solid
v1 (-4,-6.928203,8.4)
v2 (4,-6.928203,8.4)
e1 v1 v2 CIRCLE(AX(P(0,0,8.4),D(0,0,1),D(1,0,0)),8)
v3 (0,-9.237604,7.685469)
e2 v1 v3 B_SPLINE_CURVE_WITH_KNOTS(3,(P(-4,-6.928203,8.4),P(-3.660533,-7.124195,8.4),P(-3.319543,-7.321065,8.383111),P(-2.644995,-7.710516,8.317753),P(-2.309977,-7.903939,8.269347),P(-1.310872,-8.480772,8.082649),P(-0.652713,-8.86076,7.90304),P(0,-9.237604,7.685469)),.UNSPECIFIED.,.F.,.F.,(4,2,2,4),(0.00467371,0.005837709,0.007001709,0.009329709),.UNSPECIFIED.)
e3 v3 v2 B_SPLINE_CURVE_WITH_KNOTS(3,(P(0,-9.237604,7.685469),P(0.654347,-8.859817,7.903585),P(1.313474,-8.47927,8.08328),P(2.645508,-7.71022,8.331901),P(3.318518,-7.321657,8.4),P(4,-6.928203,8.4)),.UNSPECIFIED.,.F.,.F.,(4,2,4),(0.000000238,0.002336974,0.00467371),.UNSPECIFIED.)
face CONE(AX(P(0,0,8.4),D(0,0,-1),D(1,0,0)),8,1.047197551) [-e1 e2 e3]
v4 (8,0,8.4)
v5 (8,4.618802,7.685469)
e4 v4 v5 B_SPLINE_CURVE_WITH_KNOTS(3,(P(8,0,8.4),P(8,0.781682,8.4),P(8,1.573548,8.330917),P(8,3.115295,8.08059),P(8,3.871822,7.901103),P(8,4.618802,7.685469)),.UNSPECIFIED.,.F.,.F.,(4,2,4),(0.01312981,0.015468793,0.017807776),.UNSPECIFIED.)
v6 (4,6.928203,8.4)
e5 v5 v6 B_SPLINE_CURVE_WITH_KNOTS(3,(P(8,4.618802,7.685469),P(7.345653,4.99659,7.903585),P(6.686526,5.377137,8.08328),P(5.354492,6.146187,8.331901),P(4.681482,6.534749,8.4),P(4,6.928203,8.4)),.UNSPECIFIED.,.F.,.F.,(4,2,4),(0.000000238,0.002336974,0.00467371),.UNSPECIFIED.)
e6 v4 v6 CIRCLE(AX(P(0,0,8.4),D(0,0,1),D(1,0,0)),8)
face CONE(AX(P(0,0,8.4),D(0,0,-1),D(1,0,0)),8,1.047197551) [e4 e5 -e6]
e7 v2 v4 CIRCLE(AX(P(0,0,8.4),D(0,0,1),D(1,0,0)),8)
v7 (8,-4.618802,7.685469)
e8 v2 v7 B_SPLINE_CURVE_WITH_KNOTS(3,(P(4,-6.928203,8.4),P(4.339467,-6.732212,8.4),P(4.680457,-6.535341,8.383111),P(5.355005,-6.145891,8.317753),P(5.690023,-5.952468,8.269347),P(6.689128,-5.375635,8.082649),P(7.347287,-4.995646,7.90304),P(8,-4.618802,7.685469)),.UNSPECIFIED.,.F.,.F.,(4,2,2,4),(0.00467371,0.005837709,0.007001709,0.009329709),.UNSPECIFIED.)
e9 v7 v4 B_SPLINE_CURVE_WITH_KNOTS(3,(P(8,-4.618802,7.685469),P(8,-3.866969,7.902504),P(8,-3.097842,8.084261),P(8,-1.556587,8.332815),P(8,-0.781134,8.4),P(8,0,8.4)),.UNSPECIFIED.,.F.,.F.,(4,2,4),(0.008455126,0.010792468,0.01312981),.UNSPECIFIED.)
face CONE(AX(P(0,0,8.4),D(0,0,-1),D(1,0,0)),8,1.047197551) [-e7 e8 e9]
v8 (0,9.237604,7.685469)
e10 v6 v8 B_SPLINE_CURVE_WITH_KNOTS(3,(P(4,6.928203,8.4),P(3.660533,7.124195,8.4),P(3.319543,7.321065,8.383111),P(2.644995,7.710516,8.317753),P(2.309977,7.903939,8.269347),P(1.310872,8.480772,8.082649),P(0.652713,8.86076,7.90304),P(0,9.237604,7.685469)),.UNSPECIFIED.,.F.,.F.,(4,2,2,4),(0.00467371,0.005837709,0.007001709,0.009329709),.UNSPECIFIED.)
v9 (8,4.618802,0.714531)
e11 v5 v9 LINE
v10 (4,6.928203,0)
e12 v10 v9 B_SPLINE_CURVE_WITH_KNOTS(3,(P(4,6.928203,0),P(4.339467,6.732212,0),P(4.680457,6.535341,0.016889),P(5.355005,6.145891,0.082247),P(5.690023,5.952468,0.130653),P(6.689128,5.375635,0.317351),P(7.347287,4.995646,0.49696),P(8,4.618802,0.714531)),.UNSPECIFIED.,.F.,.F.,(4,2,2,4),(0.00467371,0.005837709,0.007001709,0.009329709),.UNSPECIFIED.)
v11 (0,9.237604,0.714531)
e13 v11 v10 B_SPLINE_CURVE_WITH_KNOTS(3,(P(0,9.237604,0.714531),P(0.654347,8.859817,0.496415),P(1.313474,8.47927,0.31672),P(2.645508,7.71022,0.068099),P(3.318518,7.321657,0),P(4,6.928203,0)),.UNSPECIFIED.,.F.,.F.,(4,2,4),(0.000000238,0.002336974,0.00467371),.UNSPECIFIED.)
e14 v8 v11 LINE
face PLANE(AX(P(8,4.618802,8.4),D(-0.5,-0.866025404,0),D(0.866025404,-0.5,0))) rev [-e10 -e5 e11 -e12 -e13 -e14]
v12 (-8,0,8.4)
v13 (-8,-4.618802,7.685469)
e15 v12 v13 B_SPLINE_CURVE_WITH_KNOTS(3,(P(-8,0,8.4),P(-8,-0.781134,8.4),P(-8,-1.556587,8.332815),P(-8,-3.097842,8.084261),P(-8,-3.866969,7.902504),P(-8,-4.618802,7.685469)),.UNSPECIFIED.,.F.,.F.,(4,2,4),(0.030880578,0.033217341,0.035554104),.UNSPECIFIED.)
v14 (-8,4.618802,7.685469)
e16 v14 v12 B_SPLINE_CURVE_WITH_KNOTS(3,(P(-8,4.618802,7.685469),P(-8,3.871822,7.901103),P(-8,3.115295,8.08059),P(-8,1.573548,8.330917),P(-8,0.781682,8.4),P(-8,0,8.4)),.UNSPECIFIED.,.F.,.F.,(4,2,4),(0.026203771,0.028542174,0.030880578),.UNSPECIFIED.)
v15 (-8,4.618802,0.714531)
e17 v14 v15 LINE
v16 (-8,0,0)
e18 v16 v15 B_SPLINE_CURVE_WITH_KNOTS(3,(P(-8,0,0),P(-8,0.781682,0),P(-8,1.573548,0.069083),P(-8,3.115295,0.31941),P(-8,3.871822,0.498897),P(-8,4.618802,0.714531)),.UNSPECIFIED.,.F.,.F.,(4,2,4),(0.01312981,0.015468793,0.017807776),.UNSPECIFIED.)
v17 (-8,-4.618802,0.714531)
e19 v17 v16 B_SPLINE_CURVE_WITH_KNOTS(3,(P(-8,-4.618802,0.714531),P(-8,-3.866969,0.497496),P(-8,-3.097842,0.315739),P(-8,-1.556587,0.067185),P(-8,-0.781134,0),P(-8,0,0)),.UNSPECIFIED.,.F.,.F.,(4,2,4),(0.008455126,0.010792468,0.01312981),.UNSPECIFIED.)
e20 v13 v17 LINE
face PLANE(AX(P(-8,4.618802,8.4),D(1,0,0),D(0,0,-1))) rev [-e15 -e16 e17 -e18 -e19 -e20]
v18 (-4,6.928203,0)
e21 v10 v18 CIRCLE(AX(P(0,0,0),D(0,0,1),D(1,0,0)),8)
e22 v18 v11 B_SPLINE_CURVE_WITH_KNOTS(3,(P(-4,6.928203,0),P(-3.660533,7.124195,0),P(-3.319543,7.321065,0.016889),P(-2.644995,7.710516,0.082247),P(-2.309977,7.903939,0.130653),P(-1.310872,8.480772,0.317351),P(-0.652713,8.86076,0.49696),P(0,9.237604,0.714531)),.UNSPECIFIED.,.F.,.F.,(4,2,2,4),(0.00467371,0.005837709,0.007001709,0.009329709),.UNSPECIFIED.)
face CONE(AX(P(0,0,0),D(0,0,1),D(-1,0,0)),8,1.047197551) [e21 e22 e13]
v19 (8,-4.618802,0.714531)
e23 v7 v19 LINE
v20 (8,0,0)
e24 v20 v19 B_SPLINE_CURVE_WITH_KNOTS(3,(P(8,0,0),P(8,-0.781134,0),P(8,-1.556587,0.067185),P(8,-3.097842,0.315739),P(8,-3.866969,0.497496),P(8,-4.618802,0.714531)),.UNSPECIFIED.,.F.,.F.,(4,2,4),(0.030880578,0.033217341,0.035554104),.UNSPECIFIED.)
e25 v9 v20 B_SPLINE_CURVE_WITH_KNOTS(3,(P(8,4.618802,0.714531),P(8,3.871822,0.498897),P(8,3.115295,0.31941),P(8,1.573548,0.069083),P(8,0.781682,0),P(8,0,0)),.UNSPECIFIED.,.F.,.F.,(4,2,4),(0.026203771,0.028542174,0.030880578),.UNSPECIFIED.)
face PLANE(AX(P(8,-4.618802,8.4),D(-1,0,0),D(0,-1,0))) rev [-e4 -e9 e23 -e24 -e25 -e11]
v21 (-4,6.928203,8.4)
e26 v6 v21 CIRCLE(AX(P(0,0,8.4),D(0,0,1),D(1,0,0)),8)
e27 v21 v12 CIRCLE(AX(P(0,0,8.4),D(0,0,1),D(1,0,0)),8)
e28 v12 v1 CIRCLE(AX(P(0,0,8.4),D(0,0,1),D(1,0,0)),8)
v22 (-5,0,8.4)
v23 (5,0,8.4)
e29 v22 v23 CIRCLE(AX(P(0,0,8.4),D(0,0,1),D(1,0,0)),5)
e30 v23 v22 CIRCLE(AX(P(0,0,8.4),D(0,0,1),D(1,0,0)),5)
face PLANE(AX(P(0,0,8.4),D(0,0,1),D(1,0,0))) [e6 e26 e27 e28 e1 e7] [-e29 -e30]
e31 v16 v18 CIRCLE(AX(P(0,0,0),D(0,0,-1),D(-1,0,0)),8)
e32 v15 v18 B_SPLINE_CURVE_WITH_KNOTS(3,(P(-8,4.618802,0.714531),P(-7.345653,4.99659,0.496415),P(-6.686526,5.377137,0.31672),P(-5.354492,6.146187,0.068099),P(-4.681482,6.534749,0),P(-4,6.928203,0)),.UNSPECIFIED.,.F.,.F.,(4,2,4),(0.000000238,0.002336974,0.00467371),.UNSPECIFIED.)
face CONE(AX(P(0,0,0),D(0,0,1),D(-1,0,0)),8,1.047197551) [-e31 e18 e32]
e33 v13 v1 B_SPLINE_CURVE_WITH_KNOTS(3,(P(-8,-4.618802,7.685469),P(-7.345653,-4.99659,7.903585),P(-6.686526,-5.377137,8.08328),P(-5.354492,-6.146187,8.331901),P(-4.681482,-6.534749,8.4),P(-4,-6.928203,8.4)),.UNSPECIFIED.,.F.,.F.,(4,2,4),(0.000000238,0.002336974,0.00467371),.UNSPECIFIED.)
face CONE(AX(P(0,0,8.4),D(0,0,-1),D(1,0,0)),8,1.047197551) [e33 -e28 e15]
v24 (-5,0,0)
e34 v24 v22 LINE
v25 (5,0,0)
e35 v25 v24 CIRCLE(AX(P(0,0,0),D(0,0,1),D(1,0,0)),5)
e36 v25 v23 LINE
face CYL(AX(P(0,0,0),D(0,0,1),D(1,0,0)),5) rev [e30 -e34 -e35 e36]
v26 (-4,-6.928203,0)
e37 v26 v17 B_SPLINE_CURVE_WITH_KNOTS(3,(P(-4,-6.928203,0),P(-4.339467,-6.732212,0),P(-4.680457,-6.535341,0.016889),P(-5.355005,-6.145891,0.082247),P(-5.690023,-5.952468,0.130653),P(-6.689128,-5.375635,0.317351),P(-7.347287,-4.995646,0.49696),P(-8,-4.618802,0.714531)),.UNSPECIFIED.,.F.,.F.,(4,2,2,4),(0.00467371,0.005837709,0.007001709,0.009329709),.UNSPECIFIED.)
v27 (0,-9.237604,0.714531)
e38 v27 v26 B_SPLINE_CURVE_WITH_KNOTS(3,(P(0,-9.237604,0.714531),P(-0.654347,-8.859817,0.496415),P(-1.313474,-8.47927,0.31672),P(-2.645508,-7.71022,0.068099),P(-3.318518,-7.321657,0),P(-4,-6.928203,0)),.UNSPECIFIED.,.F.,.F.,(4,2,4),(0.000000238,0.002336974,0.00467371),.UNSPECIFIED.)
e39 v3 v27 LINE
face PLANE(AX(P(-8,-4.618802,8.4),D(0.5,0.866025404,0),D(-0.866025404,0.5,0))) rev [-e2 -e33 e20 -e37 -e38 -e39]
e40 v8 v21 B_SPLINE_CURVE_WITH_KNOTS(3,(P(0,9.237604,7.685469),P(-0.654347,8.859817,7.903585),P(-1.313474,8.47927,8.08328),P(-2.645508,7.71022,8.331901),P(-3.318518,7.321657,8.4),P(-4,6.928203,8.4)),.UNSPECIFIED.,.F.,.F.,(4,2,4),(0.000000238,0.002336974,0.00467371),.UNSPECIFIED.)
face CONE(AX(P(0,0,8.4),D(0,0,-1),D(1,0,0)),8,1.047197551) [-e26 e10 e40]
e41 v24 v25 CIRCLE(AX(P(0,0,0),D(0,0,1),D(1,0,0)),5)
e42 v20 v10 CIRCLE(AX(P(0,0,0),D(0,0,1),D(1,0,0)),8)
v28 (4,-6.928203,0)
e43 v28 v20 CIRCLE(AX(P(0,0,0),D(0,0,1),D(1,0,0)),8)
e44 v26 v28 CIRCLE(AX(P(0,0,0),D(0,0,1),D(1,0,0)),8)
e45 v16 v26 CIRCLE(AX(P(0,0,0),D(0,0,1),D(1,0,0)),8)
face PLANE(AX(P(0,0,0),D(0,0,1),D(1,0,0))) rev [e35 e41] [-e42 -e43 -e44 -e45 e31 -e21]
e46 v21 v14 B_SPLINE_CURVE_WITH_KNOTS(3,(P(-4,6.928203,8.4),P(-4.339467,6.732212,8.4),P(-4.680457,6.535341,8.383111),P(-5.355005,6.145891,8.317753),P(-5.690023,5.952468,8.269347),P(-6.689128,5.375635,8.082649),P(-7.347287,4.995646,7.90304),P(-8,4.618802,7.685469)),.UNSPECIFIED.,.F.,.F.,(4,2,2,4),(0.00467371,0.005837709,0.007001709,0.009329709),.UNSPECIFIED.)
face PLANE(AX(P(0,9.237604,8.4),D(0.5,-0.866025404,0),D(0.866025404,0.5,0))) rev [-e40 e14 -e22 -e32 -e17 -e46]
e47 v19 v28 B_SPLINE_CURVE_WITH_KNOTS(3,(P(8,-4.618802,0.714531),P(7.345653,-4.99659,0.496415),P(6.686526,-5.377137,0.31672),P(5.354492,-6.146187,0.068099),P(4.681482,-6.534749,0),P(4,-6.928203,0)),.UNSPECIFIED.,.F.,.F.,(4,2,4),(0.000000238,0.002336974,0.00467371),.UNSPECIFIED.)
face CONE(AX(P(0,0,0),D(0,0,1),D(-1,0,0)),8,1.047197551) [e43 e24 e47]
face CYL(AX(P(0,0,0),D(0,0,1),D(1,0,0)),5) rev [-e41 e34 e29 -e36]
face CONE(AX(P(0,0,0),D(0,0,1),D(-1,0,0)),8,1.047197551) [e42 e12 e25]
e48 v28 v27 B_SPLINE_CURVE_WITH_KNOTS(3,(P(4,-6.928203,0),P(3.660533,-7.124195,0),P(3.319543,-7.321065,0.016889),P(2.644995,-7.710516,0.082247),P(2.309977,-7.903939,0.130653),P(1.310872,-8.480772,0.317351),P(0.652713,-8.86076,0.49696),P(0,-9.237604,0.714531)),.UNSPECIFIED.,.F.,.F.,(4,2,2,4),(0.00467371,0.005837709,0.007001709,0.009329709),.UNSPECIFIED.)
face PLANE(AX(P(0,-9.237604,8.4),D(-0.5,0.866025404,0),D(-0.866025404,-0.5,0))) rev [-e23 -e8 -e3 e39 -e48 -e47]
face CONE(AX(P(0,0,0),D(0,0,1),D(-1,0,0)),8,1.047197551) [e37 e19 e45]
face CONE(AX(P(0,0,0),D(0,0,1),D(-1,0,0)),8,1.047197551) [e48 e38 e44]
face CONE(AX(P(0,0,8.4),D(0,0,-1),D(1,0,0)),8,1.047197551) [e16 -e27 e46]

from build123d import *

# Parameters (mm, degrees)
EXTRUDE_1_DEPTH     = 8.4
SKETCH_5_R          = 5
CUT_EXTRUDE_1_DEPTH = 15.828800806
SKETCH_6_OUTSIDE_W  = 369.578
SKETCH_6_OUTSIDE_H  = 372.054
SKETCH_6_OUTSIDE_R  = 8
CUT_EXTRUDE_2_DEPTH = 100
CUT_EXTRUDE_2_DRAFT = -60
SKETCH_7_OUTSIDE_W  = 369.578
SKETCH_7_OUTSIDE_H  = 372.054
SKETCH_7_OUTSIDE_R  = 8
CUT_EXTRUDE_3_DEPTH = 100
CUT_EXTRUDE_3_DRAFT = -60


with BuildPart() as part:
    # 草图1 → 凸台-拉伸1 (new body)
    with BuildSketch(Plane.XY):
        Polygon((0, 9.237604307), (-8, 4.618802154), (-8, -4.618802154), (0, -9.237604307), (8, -4.618802154), (8, 4.618802154), align=None)
    extrude(amount=EXTRUDE_1_DEPTH)

    # 草图5 → 切除-拉伸1 (cut, through all)
    with BuildSketch(Plane.XY.offset(8.4)):
        Circle(SKETCH_5_R)
    extrude(amount=-CUT_EXTRUDE_1_DEPTH, mode=Mode.SUBTRACT)


with BuildPart() as cut_extrude_2_tool:
    # 草图6 outside → 切除-拉伸2 (with draft: the straight prism first)
    with BuildSketch(Plane.XY.offset(8.4)):
        Rectangle(SKETCH_6_OUTSIDE_W, SKETCH_6_OUTSIDE_H)
        Circle(SKETCH_6_OUTSIDE_R, mode=Mode.SUBTRACT)
    extrude(amount=-CUT_EXTRUDE_2_DEPTH)
    # 切除-拉伸2: the draft: its side faces are tilted about the plane it starts from
    cut_extrude_2_sides = [cut_extrude_2_tool.faces().sort_by_distance(p)[0] for p in [
        (0, -186.027, -41.6),
        (184.789, 0, -41.6),
        (0, 186.027, -41.6),
        (-184.789, 0, -41.6),
        (-8, 0, -41.6),
    ]]
    draft(cut_extrude_2_sides, Plane.XY.offset(8.4), CUT_EXTRUDE_2_DRAFT)


with BuildPart() as part_1:
    add(part.part)

    # 切除-拉伸2: cut by cut_extrude_2_tool
    add(cut_extrude_2_tool.part, mode=Mode.SUBTRACT)


with BuildPart() as cut_extrude_3_tool:
    # 草图7 outside → 切除-拉伸3 (with draft: the straight prism first)
    with BuildSketch(Plane(origin=(0, 0, 0), x_dir=(-1, 0, 0), z_dir=(0, 0, -1))):
        Rectangle(SKETCH_7_OUTSIDE_W, SKETCH_7_OUTSIDE_H)
        Circle(SKETCH_7_OUTSIDE_R, mode=Mode.SUBTRACT)
    extrude(amount=-CUT_EXTRUDE_3_DEPTH)
    # 切除-拉伸3: the draft: its side faces are tilted about the plane it starts from
    cut_extrude_3_sides = [cut_extrude_3_tool.faces().sort_by_distance(p)[0] for p in [
        (0, -186.027, 50),
        (-184.789, 0, 50),
        (0, 186.027, 50),
        (184.789, 0, 50),
        (8, 0, 50),
    ]]
    draft(cut_extrude_3_sides, Plane(origin=(0, 0, 0), x_dir=(-1, 0, 0), z_dir=(0, 0, -1)), CUT_EXTRUDE_3_DRAFT)


with BuildPart() as part_2:
    add(part_1.part)

    # 切除-拉伸3: cut by cut_extrude_3_tool
    add(cut_extrude_3_tool.part, mode=Mode.SUBTRACT)


solid = part_2.part
